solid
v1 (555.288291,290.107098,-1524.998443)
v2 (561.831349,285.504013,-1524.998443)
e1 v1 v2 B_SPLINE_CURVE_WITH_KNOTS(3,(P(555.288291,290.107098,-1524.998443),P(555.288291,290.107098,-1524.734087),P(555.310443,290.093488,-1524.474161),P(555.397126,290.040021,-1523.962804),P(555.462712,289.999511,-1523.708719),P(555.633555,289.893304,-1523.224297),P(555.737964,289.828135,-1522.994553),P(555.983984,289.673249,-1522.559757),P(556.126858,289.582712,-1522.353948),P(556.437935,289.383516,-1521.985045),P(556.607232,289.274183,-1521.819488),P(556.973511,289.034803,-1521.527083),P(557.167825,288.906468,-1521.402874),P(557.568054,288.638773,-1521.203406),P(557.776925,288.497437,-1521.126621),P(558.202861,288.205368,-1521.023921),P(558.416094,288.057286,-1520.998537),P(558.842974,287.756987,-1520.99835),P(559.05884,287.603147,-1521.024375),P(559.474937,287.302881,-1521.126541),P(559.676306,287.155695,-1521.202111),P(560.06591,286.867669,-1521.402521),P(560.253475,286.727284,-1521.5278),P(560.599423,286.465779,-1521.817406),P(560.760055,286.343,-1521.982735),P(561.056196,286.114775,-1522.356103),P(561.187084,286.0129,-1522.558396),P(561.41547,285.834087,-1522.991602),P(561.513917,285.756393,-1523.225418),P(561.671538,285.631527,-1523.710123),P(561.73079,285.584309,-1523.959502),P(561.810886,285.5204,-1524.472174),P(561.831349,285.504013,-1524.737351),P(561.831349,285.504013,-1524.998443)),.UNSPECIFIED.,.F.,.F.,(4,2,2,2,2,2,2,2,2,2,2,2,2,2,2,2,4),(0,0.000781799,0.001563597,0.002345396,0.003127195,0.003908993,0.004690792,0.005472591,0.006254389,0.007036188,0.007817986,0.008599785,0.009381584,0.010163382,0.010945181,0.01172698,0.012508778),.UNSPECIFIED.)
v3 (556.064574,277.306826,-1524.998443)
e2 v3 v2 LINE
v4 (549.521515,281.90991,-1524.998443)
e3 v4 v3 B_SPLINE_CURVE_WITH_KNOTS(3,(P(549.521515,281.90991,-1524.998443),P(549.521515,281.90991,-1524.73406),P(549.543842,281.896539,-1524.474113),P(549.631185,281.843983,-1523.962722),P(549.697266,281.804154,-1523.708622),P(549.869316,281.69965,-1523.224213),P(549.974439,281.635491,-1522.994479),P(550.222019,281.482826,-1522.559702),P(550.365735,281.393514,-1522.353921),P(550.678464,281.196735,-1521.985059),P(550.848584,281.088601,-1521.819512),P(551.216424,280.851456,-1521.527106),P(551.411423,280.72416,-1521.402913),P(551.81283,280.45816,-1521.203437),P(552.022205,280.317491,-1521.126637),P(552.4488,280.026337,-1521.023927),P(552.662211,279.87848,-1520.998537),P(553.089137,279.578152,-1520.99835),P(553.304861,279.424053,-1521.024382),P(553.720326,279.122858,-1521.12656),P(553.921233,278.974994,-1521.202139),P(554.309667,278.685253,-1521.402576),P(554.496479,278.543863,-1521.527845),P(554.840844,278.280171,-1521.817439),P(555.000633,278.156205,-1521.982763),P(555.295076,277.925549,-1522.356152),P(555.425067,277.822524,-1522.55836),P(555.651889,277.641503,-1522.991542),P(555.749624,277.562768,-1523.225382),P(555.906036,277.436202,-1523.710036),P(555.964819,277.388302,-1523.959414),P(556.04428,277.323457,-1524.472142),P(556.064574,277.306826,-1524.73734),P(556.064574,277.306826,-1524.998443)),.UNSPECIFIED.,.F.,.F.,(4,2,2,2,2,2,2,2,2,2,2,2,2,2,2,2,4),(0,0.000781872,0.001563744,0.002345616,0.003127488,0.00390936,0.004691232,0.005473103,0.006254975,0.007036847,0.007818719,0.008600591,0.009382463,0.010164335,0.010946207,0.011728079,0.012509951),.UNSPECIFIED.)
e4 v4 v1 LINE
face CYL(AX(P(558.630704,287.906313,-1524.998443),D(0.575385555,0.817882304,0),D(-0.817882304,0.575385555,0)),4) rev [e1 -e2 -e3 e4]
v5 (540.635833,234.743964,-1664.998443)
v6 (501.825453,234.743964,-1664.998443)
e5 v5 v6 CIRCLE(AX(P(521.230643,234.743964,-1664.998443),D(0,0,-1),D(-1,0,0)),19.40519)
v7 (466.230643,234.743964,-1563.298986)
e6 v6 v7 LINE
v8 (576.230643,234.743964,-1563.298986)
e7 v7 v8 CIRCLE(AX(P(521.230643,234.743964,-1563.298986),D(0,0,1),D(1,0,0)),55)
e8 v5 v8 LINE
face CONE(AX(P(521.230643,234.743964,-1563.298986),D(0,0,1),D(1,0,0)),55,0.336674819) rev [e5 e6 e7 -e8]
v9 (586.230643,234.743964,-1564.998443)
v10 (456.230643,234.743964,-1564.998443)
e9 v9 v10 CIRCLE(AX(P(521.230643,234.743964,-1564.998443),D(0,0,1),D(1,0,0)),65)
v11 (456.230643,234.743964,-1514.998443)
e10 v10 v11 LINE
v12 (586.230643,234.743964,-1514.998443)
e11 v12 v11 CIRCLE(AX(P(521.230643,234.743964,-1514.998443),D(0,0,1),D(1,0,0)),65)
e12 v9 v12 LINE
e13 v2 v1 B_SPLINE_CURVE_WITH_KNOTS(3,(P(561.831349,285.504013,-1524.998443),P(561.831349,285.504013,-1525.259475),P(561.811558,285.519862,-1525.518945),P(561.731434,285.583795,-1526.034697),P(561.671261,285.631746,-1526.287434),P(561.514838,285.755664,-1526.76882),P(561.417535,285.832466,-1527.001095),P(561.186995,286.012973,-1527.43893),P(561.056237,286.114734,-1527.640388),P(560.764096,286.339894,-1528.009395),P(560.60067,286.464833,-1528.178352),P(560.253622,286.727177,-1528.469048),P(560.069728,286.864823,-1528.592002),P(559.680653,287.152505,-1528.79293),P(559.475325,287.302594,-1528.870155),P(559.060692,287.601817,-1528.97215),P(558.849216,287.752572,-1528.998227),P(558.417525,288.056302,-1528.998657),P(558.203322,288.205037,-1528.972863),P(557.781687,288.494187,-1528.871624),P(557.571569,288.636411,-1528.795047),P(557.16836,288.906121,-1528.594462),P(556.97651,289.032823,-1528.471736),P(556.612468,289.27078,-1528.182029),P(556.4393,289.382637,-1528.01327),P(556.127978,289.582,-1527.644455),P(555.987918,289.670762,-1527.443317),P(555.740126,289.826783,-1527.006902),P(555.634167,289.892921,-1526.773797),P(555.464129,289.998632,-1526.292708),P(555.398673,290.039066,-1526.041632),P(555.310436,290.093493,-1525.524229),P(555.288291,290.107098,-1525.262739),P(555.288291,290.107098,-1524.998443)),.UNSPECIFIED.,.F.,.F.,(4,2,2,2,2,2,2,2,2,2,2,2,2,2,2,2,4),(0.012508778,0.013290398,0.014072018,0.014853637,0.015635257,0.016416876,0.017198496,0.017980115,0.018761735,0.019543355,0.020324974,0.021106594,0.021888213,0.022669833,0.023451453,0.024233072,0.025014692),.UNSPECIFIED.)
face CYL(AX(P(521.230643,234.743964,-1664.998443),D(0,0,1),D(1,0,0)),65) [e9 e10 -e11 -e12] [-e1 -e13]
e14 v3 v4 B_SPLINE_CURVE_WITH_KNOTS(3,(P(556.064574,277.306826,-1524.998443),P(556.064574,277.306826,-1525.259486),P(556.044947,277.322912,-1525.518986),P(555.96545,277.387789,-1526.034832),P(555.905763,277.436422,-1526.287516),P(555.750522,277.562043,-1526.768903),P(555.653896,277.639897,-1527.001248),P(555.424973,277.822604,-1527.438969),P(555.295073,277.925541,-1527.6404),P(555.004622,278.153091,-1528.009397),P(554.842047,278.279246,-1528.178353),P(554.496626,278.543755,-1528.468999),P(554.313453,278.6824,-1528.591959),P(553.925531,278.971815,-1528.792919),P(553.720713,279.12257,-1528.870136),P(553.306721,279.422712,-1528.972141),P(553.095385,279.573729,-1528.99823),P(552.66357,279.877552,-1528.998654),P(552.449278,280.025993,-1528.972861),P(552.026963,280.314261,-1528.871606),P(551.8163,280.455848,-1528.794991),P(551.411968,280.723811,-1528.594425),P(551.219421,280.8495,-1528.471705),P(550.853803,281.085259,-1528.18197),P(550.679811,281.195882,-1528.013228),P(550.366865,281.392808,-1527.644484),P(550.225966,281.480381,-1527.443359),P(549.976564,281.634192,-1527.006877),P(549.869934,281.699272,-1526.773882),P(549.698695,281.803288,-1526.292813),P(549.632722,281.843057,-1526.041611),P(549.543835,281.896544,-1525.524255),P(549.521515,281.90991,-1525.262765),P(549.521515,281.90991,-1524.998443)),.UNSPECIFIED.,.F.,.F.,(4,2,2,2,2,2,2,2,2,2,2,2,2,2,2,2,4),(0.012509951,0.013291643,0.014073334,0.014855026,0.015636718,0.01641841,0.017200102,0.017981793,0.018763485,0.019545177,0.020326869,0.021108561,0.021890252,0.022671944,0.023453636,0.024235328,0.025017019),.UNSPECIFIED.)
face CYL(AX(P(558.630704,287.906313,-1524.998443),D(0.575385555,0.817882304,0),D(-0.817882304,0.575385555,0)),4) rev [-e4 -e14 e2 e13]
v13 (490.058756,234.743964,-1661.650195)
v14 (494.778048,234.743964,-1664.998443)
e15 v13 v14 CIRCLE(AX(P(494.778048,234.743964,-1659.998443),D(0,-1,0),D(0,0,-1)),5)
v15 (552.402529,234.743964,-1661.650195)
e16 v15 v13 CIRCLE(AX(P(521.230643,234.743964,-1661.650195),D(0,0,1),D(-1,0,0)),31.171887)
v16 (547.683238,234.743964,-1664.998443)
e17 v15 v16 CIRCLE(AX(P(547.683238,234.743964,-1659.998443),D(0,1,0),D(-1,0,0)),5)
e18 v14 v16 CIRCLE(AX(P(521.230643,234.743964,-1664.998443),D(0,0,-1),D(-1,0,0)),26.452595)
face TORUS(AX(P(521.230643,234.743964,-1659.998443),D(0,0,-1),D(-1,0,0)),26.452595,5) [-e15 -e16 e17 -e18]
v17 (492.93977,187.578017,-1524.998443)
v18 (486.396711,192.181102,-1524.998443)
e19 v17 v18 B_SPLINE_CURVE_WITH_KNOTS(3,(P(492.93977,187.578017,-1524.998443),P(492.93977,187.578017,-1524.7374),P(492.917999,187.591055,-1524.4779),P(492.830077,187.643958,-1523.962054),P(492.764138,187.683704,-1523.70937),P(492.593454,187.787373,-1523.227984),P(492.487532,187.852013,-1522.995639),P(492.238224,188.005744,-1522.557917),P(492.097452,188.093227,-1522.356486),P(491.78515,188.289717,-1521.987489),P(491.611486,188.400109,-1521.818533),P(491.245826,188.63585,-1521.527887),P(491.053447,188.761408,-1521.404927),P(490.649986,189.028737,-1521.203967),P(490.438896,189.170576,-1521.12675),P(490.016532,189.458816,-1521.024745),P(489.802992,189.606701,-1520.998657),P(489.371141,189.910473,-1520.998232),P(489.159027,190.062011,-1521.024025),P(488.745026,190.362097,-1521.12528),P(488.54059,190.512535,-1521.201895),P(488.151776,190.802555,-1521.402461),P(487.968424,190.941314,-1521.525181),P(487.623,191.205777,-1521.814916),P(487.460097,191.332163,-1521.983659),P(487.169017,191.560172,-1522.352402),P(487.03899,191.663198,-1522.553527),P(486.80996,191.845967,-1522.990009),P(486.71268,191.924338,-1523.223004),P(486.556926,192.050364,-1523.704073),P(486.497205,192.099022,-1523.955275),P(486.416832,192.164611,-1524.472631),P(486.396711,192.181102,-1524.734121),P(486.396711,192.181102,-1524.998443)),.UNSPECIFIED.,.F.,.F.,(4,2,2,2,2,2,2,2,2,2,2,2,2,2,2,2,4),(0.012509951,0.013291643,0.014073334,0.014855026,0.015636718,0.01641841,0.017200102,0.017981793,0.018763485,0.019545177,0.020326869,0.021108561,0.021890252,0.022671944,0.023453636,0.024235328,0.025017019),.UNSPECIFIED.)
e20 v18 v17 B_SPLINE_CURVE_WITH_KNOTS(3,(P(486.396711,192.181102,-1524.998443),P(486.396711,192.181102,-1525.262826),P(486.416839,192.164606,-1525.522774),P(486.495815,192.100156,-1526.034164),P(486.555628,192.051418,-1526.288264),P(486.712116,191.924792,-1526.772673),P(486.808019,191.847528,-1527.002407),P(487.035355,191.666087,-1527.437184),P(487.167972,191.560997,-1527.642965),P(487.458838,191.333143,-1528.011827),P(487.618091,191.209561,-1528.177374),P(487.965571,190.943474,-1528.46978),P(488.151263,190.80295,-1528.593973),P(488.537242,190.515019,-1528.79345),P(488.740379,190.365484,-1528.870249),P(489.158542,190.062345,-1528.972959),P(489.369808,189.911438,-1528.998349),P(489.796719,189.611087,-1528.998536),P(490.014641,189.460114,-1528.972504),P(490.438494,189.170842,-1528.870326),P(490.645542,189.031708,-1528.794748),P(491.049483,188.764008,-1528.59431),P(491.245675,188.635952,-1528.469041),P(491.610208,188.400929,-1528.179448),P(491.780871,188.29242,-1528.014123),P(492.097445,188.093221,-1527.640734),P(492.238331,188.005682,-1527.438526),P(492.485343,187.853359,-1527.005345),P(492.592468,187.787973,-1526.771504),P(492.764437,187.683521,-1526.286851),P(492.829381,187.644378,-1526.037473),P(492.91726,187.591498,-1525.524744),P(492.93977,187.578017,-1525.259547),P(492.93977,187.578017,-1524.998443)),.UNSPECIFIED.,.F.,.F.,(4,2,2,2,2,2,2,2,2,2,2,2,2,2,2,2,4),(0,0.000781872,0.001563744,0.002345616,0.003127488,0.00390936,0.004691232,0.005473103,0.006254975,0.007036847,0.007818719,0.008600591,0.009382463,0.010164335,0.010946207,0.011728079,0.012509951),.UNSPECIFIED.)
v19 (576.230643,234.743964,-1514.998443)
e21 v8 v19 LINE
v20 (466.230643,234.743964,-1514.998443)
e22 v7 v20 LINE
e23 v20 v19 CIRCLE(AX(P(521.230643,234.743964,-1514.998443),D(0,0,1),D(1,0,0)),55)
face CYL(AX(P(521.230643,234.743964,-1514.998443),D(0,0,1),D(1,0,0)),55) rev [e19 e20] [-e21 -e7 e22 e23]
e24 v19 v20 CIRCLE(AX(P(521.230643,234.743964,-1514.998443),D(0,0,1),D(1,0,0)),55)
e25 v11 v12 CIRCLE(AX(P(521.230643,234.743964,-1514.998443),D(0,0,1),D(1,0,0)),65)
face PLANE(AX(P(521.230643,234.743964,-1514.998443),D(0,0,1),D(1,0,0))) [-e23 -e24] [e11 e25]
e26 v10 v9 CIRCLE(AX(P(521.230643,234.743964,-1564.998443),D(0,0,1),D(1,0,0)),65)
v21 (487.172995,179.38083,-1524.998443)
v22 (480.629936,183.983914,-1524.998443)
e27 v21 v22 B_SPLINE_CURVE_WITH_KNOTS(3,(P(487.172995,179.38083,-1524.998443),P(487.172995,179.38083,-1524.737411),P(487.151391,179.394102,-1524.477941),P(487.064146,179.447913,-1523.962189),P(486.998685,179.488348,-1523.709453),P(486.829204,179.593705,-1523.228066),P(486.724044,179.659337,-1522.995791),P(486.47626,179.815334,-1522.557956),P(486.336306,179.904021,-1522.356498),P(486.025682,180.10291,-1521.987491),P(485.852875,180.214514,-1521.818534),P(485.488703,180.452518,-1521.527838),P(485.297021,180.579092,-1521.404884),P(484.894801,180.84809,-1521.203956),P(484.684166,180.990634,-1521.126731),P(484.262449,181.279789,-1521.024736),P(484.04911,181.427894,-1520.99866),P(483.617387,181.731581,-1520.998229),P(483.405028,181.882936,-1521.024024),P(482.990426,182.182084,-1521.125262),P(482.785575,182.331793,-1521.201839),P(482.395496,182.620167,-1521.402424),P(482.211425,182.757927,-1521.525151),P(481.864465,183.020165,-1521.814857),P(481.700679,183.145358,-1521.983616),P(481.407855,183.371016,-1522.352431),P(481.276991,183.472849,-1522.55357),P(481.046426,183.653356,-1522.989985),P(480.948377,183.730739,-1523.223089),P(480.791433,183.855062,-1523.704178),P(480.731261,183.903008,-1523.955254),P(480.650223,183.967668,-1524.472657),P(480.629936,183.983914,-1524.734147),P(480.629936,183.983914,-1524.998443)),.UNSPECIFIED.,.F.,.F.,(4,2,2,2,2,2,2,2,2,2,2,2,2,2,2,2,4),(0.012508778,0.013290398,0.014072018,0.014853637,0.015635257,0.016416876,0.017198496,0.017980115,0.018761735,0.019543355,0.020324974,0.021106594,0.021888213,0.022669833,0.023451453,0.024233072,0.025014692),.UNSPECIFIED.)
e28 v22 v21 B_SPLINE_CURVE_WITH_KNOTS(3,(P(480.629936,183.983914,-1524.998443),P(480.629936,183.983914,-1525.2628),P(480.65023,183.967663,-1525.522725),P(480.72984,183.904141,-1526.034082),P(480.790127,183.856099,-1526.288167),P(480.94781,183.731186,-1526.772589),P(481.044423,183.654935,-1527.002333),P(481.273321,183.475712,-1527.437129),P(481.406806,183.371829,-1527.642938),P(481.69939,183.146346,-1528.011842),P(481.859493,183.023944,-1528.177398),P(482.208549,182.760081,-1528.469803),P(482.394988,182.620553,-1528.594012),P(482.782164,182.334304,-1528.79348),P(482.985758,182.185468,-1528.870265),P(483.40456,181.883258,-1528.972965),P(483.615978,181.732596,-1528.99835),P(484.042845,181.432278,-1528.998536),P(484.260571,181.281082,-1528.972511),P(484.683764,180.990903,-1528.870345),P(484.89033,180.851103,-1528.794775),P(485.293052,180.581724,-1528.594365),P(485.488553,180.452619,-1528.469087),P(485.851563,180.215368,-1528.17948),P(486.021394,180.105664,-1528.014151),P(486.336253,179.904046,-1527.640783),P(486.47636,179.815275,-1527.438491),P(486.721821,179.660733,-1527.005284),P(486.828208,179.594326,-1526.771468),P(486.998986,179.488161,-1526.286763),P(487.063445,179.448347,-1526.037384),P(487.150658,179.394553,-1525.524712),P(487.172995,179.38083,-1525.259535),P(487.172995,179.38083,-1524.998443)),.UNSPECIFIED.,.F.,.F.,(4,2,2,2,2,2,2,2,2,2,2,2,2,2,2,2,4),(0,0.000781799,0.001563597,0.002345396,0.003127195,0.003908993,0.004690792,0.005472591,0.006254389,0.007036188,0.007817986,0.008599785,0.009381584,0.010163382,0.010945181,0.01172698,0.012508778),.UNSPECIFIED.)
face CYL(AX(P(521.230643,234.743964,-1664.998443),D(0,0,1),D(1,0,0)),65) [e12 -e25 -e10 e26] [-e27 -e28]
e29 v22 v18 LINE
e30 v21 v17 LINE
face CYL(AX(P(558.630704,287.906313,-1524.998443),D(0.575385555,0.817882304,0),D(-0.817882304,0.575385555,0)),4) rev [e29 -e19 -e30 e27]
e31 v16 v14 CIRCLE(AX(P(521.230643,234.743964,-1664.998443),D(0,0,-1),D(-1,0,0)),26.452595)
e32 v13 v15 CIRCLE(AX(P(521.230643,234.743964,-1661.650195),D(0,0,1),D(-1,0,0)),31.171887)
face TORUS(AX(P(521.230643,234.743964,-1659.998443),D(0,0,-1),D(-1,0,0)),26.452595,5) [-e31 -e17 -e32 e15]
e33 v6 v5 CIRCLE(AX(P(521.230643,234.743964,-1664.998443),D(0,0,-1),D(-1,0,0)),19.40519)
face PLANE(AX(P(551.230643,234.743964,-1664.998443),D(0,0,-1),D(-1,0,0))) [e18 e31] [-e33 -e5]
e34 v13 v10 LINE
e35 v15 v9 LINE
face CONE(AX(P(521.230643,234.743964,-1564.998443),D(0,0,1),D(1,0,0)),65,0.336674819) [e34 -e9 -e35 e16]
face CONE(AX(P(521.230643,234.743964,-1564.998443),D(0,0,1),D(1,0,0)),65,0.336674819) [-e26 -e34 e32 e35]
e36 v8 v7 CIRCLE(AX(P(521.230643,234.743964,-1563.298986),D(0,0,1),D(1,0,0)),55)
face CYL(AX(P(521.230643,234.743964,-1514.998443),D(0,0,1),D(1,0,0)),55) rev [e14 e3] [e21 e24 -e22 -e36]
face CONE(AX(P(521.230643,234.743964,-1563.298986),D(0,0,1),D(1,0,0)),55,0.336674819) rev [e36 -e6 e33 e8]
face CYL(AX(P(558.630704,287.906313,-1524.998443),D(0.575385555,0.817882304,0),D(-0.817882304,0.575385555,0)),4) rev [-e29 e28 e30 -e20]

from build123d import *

# Parameters (mm, degrees)
M100_CLEARANCE_HOLE1_D       = 110
M100_CLEARANCE_HOLE1_DEPTH   = 48.300542714
M100_CLEARANCE_HOLE1_TIP     = 157.142859071
F_8_0_8_DIAMETER_HOLE1_D     = 8
F_8_0_8_DIAMETER_HOLE1_DEPTH = 140.145647392
FILLET1_R                    = 5


with BuildPart() as part:
    # Sketch1 → Revolve1 (revolve)
    with BuildSketch(Plane(origin=(0, 234.743963655, 0), x_dir=(1, 0, 0), z_dir=(0, 1, 0))):
        Polygon((551.230642584, 1664.998443067), (521.230642584, 1664.998443067), (521.230642584, 1514.998443067), (586.230642584, 1514.998443067), (586.230642584, 1564.998443067), align=None)
    revolve(axis=Axis((521.230642584, 234.743963655, -1664.998443067), (0, 0, 1)))

    # M100 clearance hole1
    with Locations(Plane.XY.offset(-1514.998443067)):
        with Locations((521.230642584, 234.743963655)):
            Hole(M100_CLEARANCE_HOLE1_D / 2, depth=M100_CLEARANCE_HOLE1_DEPTH)
            with Locations((0, 0, -(M100_CLEARANCE_HOLE1_DEPTH + M100_CLEARANCE_HOLE1_TIP / 2))):  # 38.580092° drill point
                Cone(0, M100_CLEARANCE_HOLE1_D / 2, M100_CLEARANCE_HOLE1_TIP, mode=Mode.SUBTRACT)

    # Ø8.0 (8) diameter hole1
    with Locations(Plane(origin=(558.630703666, 287.906313406, -1524.998443067), x_dir=(0.817882303865, -0.575385555106, 0), z_dir=(0.575385555106, 0.817882303865, 0))):
        with Locations((0, 0)):
            Hole(F_8_0_8_DIAMETER_HOLE1_D / 2, depth=F_8_0_8_DIAMETER_HOLE1_DEPTH)

    # Fillet1
    fillet1_edges = [part.edges().sort_by_distance(p)[0] for p in [
        (491.230642584, 234.743963655, -1664.998443067),
    ]]
    fillet(fillet1_edges, radius=FILLET1_R)


solid = part.part
